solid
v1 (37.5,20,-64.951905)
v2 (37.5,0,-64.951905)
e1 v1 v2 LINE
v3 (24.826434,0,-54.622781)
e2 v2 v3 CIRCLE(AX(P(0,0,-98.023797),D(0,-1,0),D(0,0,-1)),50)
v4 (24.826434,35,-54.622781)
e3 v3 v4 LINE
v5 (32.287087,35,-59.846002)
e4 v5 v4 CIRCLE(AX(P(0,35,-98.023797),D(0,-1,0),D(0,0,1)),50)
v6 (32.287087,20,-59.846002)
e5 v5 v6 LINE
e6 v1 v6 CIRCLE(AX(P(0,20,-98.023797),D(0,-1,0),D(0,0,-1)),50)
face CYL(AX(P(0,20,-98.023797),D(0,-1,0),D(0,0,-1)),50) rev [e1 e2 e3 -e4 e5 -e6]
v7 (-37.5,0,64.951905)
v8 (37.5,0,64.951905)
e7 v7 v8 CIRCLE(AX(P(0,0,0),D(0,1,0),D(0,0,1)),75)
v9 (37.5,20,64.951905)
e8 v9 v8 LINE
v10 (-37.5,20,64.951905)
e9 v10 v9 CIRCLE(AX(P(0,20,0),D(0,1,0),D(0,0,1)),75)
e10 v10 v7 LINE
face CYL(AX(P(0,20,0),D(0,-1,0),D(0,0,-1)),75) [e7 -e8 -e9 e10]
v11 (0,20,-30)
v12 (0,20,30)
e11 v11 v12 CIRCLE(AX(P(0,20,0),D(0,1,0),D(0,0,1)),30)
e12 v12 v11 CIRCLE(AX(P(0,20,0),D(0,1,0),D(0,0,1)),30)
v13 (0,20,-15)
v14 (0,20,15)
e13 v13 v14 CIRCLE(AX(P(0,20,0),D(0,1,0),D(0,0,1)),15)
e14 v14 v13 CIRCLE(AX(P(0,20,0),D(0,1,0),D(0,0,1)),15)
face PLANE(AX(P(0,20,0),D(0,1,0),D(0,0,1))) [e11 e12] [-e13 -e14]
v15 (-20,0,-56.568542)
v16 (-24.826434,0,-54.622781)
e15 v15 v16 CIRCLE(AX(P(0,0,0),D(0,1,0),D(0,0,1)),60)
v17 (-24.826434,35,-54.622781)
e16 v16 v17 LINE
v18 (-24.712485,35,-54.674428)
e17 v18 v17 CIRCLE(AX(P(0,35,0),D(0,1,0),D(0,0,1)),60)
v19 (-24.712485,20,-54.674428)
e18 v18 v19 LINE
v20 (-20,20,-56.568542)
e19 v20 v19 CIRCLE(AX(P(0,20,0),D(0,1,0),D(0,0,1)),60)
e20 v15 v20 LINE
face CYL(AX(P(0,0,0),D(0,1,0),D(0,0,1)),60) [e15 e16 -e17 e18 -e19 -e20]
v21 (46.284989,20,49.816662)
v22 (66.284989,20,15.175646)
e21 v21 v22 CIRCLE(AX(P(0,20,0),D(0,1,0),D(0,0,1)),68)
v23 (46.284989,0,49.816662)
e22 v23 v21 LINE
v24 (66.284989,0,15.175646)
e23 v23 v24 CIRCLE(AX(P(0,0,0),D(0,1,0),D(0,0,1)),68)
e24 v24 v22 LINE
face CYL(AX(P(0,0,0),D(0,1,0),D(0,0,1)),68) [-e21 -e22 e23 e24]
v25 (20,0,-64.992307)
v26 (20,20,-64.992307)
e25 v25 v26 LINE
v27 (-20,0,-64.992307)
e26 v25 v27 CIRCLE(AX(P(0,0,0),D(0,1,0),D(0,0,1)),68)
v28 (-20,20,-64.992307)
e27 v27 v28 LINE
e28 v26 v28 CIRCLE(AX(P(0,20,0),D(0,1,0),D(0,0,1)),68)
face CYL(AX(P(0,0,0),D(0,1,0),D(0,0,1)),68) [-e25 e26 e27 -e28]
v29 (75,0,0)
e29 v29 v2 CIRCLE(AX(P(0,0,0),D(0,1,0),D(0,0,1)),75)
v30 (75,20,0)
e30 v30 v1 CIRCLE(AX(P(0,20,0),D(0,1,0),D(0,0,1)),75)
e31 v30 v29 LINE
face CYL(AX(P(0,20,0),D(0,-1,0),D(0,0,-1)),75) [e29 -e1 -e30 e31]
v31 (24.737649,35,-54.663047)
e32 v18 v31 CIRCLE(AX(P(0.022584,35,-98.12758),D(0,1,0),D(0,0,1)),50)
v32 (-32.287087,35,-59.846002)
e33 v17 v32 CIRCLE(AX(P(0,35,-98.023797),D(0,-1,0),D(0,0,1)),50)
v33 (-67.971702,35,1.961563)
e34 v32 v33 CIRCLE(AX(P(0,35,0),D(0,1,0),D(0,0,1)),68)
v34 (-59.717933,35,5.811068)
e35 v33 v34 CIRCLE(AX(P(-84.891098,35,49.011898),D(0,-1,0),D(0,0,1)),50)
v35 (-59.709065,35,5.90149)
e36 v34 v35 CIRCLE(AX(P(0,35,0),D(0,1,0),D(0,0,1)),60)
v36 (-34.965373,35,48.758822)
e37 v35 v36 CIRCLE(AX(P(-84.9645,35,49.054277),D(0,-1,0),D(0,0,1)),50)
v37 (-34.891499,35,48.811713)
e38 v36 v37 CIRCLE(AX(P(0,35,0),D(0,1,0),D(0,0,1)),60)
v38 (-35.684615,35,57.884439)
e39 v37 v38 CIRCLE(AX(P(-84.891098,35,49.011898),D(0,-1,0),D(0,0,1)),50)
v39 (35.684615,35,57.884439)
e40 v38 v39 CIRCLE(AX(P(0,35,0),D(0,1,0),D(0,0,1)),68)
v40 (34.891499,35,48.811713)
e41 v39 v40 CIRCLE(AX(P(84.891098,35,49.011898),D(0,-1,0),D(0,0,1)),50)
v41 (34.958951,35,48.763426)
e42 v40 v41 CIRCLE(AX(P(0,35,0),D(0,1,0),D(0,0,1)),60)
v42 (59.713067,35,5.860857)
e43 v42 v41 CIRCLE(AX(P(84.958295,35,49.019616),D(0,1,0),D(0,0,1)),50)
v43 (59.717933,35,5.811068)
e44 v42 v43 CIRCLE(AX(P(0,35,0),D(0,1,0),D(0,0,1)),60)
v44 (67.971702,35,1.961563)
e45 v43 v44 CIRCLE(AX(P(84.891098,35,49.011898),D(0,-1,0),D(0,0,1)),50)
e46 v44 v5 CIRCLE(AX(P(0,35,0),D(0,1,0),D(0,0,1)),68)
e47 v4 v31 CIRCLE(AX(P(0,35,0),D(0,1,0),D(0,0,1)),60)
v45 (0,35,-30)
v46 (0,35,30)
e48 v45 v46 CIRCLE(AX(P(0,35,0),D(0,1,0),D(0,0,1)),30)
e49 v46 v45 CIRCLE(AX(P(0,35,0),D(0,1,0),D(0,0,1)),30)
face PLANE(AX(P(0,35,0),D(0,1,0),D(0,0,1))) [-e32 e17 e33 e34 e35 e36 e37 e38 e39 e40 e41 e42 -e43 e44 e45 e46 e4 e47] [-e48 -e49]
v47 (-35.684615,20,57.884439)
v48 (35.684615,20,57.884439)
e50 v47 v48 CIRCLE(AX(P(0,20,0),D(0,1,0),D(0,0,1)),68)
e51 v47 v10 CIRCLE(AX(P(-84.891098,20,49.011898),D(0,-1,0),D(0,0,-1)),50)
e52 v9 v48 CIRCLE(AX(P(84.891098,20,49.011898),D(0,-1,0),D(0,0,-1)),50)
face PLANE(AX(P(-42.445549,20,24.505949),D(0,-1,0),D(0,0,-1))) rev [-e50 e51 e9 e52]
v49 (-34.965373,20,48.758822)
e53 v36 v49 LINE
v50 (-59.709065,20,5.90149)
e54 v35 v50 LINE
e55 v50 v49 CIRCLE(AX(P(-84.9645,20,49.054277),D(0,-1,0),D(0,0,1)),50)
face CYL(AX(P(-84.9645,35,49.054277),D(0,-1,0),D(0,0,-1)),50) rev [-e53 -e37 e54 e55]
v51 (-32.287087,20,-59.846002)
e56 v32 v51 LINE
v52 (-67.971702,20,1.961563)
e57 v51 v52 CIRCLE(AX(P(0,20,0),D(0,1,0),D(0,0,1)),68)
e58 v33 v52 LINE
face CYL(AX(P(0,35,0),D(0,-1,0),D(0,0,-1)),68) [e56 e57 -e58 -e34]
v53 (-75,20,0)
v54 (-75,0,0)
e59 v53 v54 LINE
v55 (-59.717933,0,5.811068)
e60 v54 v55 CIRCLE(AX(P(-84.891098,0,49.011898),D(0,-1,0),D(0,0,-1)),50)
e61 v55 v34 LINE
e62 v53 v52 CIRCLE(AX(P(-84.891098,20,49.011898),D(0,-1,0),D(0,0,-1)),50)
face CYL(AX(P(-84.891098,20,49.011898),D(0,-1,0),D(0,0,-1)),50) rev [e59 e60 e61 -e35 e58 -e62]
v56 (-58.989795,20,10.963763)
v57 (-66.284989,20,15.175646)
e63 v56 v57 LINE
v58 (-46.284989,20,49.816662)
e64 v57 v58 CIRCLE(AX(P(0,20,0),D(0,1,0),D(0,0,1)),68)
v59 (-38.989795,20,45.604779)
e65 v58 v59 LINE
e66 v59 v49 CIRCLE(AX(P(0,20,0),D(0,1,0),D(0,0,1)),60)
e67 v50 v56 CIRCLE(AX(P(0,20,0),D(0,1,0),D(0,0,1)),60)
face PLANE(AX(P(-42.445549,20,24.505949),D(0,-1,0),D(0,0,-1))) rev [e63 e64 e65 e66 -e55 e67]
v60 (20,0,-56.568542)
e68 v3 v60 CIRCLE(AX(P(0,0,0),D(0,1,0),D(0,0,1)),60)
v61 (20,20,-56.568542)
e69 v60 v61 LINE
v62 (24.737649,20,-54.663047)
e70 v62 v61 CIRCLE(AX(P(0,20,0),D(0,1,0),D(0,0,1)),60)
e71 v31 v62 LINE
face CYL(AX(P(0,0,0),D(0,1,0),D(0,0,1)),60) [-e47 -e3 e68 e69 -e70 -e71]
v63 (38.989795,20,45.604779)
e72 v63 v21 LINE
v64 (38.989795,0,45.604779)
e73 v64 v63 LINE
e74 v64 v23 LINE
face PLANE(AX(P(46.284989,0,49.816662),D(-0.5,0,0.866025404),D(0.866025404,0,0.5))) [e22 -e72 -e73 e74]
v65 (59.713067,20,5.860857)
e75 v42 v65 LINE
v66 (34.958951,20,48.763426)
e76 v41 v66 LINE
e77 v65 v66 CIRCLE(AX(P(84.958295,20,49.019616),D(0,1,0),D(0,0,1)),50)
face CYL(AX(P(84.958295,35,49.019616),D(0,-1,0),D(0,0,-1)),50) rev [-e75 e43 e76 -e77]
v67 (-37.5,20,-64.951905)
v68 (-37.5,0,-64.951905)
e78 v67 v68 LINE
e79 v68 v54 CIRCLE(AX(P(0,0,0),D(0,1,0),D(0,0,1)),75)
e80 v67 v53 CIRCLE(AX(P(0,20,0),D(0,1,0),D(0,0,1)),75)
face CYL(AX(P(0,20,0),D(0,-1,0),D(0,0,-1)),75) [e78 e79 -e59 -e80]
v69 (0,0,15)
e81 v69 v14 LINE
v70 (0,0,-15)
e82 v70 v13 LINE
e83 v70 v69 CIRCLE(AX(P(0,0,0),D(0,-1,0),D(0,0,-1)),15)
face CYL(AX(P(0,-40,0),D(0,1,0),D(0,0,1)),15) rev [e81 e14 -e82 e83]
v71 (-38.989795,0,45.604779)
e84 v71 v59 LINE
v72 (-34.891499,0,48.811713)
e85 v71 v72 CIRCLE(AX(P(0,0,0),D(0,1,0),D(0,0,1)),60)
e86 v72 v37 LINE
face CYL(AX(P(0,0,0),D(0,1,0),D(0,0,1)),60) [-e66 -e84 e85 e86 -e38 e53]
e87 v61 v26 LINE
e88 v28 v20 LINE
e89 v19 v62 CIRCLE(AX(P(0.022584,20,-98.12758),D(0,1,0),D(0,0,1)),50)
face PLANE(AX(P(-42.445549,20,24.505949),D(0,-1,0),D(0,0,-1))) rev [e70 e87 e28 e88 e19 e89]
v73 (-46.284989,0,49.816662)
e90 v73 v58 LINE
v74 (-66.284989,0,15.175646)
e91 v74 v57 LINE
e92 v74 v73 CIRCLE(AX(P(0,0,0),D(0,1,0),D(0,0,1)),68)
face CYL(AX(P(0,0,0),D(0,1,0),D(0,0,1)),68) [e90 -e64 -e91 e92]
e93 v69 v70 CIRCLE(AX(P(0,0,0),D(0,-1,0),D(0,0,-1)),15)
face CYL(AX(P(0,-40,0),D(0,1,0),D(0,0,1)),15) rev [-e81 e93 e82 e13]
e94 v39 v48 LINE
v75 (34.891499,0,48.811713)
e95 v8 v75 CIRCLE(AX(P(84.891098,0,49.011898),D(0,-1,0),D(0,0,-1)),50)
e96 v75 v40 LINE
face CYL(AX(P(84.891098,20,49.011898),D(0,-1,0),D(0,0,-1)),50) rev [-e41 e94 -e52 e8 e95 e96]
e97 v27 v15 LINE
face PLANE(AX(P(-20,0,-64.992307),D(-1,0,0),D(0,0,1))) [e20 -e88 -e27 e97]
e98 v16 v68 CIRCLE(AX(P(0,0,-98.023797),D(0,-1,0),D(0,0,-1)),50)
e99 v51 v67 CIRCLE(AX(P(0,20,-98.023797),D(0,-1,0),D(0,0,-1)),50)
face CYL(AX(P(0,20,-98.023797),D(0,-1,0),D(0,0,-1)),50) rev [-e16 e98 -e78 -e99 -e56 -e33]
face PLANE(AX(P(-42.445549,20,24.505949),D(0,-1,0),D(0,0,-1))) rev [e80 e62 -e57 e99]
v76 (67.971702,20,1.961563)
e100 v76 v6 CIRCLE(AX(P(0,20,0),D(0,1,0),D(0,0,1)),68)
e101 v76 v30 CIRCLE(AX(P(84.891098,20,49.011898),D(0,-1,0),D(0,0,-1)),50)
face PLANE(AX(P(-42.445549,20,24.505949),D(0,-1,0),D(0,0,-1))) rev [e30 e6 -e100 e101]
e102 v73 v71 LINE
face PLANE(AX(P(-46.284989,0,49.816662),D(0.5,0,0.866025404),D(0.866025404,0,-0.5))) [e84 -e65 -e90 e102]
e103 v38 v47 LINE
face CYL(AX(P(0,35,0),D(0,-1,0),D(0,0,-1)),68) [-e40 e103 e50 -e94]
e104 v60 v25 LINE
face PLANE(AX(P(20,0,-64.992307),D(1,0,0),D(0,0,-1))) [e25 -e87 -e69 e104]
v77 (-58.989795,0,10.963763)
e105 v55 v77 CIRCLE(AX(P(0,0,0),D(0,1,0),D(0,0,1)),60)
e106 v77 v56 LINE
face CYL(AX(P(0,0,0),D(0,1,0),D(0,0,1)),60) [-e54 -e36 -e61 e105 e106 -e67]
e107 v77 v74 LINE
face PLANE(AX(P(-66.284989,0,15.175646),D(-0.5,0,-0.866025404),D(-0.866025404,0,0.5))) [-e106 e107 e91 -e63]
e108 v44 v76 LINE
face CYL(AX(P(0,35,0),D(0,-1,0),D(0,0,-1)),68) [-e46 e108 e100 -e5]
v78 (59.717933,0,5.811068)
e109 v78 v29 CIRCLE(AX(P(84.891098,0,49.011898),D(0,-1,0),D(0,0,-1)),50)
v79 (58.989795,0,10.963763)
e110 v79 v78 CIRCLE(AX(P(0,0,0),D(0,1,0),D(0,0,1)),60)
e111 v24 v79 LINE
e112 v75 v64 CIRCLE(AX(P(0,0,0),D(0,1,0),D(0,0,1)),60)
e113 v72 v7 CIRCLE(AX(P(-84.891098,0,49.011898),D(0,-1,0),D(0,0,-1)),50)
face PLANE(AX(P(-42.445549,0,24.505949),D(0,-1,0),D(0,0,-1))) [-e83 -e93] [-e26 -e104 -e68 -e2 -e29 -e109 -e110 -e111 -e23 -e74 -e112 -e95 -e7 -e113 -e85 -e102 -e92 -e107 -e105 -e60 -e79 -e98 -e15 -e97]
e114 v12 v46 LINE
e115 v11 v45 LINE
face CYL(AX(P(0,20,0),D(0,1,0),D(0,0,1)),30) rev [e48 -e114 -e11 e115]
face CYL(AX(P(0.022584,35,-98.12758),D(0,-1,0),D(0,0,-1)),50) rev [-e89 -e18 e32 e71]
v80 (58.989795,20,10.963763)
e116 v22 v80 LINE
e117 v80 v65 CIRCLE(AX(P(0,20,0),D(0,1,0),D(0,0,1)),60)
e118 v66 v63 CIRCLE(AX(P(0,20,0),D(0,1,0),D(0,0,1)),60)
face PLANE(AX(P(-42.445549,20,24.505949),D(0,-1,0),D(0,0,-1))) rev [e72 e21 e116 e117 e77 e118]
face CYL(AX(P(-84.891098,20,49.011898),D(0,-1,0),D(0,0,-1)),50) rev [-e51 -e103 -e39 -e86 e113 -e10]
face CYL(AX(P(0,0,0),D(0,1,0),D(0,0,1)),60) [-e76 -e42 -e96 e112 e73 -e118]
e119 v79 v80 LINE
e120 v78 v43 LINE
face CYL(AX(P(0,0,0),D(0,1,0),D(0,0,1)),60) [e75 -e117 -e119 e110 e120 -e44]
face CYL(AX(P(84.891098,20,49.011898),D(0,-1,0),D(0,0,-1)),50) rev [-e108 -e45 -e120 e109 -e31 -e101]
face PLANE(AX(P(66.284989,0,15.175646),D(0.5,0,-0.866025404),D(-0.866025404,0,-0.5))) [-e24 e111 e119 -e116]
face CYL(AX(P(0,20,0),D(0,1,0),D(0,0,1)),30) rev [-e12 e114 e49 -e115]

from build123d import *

# Parameters (mm, degrees)
LOBED_BASE_20MM_DEPTH          = 20
NOTCHED_START                  = -20
NOTCHED_STEP_BOSS_20MM_DEPTH   = 20
LOBED_TOP_STEP_BOSS_15MM_DEPTH = 15
COUNTERBORE_PROFILE_60_R       = 30
COUNTERBORE_60X15_DEPTH        = 15
CENTER_BORE_PROFILE_30_R       = 15
CENTER_BORE_30_DEPTH           = 60


with BuildPart() as part:
    # Lobed Base Profile → Lobed Base 20mm (new body)
    with BuildSketch(Plane(origin=(0, 0, 0), x_dir=(1, 0, 0), z_dir=(0, 1, 0))):
        with BuildLine():
            ThreePointArc((-37.5, 64.951905284), (-64.951905284, 37.5), (-75, 0))
            ThreePointArc((-75, 0), (-41.589827904, -24.011898336), (-37.5, -64.951905284))
            ThreePointArc((-37.5, -64.951905284), (0, -75), (37.5, -64.951905284))
            ThreePointArc((37.5, -64.951905284), (41.589827904, -24.011898336), (75, 0))
            ThreePointArc((75, 0), (64.951905284, 37.5), (37.5, 64.951905284))
            ThreePointArc((37.5, 64.951905284), (0, 48.023796672), (-37.5, 64.951905284))
        make_face()
    extrude(amount=LOBED_BASE_20MM_DEPTH)

    # Notched Step Profile → Notched Step Boss 20mm (add)
    with BuildSketch(Plane(origin=(0, 20, 0), x_dir=(1, 0, 0), z_dir=(0, 1, 0)).offset(NOTCHED_START)):
        with BuildLine():
            Line((66.284989118, -15.175645543), (58.989794856, -10.963763172))
            ThreePointArc((58.989794856, -10.963763172), (59.409752684, -8.395313338), (59.717932727, -5.811067957))
            ThreePointArc((59.717932727, -5.811067957), (41.589827904, -24.011898336), (34.891498837, -48.811712825))
            ThreePointArc((34.891498837, -48.811712825), (36.975430965, -47.252698388), (38.989794856, -45.604779323))
            Line((38.989794856, -45.604779323), (46.284989118, -49.816661694))
            ThreePointArc((46.284989118, -49.816661694), (58.889727457, -34), (66.284989118, -15.175645543))
        make_face()
        with BuildLine():
            Line((20, 64.992307237), (20, 56.568542495))
            ThreePointArc((20, 56.568542495), (22.434321719, 55.648011726), (24.82643389, 54.622780782))
            ThreePointArc((24.82643389, 54.622780782), (0, 48.023796672), (-24.82643389, 54.622780782))
            ThreePointArc((-24.82643389, 54.622780782), (-22.434321719, 55.648011726), (-20, 56.568542495))
            Line((-20, 56.568542495), (-20, 64.992307237))
            ThreePointArc((-20, 64.992307237), (0, 68), (20, 64.992307237))
        make_face()
        with BuildLine():
            Line((-46.284989118, -49.816661694), (-38.989794856, -45.604779323))
            ThreePointArc((-38.989794856, -45.604779323), (-36.975430965, -47.252698388), (-34.891498837, -48.811712825))
            ThreePointArc((-34.891498837, -48.811712825), (-41.589827904, -24.011898336), (-59.717932727, -5.811067957))
            ThreePointArc((-59.717932727, -5.811067957), (-59.409752684, -8.395313338), (-58.989794856, -10.963763172))
            Line((-58.989794856, -10.963763172), (-66.284989118, -15.175645543))
            ThreePointArc((-66.284989118, -15.175645543), (-58.889727457, -34), (-46.284989118, -49.816661694))
        make_face()
    extrude(amount=NOTCHED_STEP_BOSS_20MM_DEPTH)

    # Lobed Top Step Profile → Lobed Top Step Boss 15mm (add)
    with BuildSketch(Plane(origin=(0, 20, 0), x_dir=(1, 0, 0), z_dir=(0, 1, 0))):
        with BuildLine():
            ThreePointArc((-35.684614564, -57.884439044), (-34.845932731, -58.393158607), (-34, -58.889727457))
            ThreePointArc((-34, -58.889727457), (0, -68), (34, -58.889727457))
            ThreePointArc((34, -58.889727457), (34.845932731, -58.393158607), (35.684614564, -57.884439044))
            ThreePointArc((35.684614564, -57.884439044), (35.081055876, -53.366171445), (34.891498837, -48.811712825))
            ThreePointArc((34.891498837, -48.811712825), (34.925233252, -48.78758123), (34.958950977, -48.763426321))
            ThreePointArc((34.958950977, -48.763426321), (41.65016617, -24.031498852), (59.713066847, -5.860857251))
            ThreePointArc((59.713066847, -5.860857251), (59.715504976, -5.835963111), (59.717932727, -5.811067957))
            ThreePointArc((59.717932727, -5.811067957), (63.756988112, -3.697999858), (67.971701978, -1.961563214))
            ThreePointArc((67.971701978, -1.961563214), (67.992925126, -0.98088366), (68, 0))
            ThreePointArc((68, 0), (58.393158607, 34.845932731), (32.287087414, 59.846002258))
            ThreePointArc((32.287087414, 59.846002258), (28.675932236, 57.064171303), (24.82643389, 54.622780782))
            ThreePointArc((24.82643389, 54.622780782), (24.782049597, 54.642932002), (24.737648948, 54.663047157))
            ThreePointArc((24.737648948, 54.663047157), (0.01107673, 48.127580971), (-24.712484549, 54.674428277))
            ThreePointArc((-24.712484549, 54.674428277), (-24.769472681, 54.648634229), (-24.82643389, 54.622780782))
            ThreePointArc((-24.82643389, 54.622780782), (-28.675932236, 57.064171303), (-32.287087414, 59.846002258))
            ThreePointArc((-32.287087414, 59.846002258), (-58.889727457, 34), (-67.971701978, -1.961563214))
            ThreePointArc((-67.971701978, -1.961563214), (-63.756988112, -3.697999858), (-59.717932727, -5.811067957))
            ThreePointArc((-59.717932727, -5.811067957), (-59.713515872, -5.856280575), (-59.709064787, -5.901489836))
            ThreePointArc((-59.709064787, -5.901489836), (-41.66322938, -24.054276698), (-34.965372512, -48.758822023))
            ThreePointArc((-34.965372512, -48.758822023), (-34.928445686, -48.785281407), (-34.891498837, -48.811712825))
            ThreePointArc((-34.891498837, -48.811712825), (-35.081055876, -53.366171445), (-35.684614564, -57.884439044))
        make_face()
    extrude(amount=LOBED_TOP_STEP_BOSS_15MM_DEPTH)

    # Counterbore Profile Ø60 → Counterbore Ø60x15 (cut)
    with BuildSketch(Plane(origin=(0, 35, 0), x_dir=(1, 0, 0), z_dir=(0, 1, 0))):
        with Locations(Location((0, 0, 0), (0, 0, 270))):
            Circle(COUNTERBORE_PROFILE_60_R)
    extrude(amount=-COUNTERBORE_60X15_DEPTH, mode=Mode.SUBTRACT)

    # Center Bore Profile Ø30 → Center Bore Ø30 (cut)
    with BuildSketch(Plane(origin=(0, 20, 0), x_dir=(1, 0, 0), z_dir=(0, 1, 0))):
        with Locations(Location((0, 0, 0), (0, 0, 270))):
            Circle(CENTER_BORE_PROFILE_30_R)
    extrude(amount=-CENTER_BORE_30_DEPTH, mode=Mode.SUBTRACT)


solid = part.part
